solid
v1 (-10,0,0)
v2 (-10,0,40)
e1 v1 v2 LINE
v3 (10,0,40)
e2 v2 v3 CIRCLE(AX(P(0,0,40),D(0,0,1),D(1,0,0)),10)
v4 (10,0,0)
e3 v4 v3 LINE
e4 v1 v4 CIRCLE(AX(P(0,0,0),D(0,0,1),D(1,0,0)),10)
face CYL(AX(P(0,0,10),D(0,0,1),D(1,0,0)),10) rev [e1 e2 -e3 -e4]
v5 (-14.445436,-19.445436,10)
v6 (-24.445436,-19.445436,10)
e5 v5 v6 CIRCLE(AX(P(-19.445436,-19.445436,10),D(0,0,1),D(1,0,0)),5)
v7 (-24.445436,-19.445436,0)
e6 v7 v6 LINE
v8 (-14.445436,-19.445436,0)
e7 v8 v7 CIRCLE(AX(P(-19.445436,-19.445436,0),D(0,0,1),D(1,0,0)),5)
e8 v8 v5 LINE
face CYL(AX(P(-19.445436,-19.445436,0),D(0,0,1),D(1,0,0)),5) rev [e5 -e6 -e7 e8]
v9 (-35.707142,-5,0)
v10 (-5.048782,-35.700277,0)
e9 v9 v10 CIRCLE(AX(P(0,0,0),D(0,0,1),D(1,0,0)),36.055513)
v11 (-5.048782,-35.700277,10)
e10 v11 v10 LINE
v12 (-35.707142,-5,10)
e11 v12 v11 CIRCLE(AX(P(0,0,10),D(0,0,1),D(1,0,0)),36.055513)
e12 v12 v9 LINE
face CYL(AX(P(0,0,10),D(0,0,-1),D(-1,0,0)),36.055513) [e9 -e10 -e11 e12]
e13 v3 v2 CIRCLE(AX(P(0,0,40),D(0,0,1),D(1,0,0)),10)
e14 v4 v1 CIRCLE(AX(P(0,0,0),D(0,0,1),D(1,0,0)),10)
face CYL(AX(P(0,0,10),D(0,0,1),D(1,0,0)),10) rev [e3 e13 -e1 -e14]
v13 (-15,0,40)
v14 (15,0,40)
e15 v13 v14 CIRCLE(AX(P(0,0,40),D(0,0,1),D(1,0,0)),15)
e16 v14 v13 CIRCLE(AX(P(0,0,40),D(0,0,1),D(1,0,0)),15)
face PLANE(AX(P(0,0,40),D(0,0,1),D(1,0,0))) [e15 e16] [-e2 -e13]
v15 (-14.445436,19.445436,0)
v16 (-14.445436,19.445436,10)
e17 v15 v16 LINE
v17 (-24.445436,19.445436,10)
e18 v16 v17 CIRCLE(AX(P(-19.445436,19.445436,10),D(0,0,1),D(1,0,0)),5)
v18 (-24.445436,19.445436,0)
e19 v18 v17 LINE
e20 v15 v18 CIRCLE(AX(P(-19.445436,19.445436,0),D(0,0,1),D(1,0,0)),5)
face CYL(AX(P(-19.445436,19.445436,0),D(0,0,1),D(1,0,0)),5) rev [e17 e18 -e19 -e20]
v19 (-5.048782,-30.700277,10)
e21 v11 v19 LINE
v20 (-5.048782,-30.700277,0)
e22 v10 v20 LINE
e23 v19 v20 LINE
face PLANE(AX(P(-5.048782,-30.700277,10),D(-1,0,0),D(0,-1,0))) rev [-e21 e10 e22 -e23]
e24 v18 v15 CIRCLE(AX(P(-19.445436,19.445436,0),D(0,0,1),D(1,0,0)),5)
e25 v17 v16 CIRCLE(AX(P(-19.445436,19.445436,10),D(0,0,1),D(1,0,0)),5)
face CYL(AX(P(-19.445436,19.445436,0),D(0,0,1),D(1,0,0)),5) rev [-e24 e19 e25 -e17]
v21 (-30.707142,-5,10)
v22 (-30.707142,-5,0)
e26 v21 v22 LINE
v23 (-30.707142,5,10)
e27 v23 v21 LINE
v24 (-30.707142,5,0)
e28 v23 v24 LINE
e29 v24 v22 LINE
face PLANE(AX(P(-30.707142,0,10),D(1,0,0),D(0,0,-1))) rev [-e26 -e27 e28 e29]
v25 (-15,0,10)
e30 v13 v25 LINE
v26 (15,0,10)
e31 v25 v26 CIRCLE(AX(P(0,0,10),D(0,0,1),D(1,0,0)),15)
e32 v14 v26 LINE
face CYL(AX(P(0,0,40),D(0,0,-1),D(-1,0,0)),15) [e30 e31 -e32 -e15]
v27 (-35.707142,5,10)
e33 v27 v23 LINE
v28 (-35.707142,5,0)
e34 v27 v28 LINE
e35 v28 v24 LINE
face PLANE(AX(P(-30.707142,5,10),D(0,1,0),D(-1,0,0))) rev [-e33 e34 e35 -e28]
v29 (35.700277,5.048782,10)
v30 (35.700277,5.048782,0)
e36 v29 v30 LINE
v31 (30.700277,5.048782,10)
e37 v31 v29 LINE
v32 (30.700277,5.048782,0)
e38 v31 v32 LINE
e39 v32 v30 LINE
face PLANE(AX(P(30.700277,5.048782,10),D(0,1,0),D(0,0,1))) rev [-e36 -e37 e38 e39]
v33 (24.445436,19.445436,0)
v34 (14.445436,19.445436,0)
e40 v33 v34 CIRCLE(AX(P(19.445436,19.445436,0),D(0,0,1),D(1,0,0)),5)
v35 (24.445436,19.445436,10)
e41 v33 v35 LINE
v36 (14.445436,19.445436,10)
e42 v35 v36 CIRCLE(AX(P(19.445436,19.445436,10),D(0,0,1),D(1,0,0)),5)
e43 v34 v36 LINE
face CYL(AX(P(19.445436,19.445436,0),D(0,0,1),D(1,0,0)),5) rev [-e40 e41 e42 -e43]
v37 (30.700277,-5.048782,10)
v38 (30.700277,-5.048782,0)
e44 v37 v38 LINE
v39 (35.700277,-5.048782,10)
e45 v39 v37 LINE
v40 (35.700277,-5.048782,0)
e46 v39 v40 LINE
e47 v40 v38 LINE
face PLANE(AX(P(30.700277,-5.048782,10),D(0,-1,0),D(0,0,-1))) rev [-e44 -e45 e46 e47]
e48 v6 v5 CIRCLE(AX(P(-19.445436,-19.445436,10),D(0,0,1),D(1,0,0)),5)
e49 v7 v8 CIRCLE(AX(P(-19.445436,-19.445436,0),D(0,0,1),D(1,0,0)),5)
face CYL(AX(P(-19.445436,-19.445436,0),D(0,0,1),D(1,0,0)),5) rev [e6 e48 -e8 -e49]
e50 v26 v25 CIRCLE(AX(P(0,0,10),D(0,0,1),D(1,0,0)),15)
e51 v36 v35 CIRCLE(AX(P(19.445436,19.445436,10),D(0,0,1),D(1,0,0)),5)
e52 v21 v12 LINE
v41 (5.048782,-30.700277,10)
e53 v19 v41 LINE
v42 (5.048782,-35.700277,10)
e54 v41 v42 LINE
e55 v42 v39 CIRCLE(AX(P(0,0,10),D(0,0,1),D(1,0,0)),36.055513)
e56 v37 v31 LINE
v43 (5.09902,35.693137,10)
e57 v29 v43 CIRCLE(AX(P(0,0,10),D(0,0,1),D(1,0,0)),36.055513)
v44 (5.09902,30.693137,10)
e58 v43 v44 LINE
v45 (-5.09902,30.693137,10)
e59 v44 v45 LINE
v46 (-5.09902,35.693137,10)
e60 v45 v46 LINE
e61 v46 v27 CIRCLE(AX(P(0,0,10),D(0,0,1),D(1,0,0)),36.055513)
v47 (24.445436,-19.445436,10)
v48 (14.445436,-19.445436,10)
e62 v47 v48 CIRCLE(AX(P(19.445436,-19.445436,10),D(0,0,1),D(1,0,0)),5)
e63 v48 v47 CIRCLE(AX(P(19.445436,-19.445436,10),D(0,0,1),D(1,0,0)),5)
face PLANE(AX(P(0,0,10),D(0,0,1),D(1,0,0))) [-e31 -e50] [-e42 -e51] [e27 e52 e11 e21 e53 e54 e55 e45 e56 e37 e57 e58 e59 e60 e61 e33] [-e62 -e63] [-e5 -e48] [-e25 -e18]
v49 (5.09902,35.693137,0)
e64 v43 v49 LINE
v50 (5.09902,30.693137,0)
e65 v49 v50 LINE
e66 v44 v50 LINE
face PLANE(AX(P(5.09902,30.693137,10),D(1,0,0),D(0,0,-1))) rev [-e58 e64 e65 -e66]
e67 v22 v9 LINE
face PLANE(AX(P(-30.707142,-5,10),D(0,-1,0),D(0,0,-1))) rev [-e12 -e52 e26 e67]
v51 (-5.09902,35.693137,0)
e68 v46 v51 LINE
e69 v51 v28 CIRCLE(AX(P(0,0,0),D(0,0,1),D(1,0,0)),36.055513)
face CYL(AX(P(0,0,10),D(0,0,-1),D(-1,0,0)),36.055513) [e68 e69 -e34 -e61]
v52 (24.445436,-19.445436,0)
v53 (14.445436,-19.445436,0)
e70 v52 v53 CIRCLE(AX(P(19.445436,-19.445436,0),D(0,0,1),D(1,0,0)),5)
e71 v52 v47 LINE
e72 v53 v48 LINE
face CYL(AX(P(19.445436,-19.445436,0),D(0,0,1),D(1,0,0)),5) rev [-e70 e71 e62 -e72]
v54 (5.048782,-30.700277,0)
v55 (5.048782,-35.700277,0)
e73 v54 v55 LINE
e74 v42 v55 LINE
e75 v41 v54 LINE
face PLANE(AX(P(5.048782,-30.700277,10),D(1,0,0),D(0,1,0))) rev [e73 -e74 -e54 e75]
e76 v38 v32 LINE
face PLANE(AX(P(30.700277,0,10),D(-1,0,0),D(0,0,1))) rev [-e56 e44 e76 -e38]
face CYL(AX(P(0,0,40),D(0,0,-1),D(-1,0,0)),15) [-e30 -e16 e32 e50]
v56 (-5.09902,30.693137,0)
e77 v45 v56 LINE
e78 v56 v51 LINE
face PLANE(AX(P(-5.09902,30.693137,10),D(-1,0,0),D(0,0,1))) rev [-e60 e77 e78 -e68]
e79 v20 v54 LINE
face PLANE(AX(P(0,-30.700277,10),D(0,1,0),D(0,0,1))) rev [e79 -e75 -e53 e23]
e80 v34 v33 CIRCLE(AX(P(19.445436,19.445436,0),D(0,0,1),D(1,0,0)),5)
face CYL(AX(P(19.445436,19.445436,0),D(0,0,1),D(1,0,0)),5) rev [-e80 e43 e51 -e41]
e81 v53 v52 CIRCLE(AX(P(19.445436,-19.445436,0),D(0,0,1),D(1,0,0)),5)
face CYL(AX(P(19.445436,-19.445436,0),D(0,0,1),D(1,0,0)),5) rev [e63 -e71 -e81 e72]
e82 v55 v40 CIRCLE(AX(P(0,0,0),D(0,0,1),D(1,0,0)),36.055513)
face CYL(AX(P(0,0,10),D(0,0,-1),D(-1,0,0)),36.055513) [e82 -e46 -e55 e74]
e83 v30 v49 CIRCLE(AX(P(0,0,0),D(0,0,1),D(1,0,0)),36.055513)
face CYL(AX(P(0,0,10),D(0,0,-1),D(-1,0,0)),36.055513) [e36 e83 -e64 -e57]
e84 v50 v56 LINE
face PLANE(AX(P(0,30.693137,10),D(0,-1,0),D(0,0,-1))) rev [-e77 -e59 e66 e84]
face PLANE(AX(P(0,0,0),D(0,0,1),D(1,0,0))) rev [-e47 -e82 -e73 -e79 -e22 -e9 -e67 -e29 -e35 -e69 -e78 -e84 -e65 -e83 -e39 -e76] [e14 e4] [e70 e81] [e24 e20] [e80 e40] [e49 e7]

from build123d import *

# Parameters (mm, degrees)
FLANGE_PLATE_DEPTH         = 10
MOUNTING_HOLES_SKETCH_R    = 5
MOUNTING_HOLES_4X_10_DEPTH = 10
HUB_SKETCH_R               = 15
HUB_30_DEPTH               = 30
HUB_BORE_SKETCH_R          = 10
HUB_BORE_20_DEPTH          = 30
FLANGE_BORE_SKETCH_R       = 10
FLANGE_BORE_20_DEPTH       = 30


with BuildPart() as part:
    # Flange Profile Sketch → Flange Plate (new body)
    with BuildSketch(Plane.XY):
        with BuildLine():
            Line((0, 30.693136595), (5.099019514, 30.693136595))
            Line((5.099019514, 30.693136595), (5.099019514, 35.693136595))
            ThreePointArc((5.099019514, 35.693136595), (25.513031554, 25.477150958), (35.700277365, 5.048781643))
            Line((35.700277365, 5.048781643), (30.700277365, 5.048781643))
            Line((30.700277365, 5.048781643), (30.700277365, 0))
            Line((30.700277365, 0), (30.700277365, -5.048781643))
            Line((30.700277365, -5.048781643), (35.700277365, -5.048781643))
            ThreePointArc((35.700277365, -5.048781643), (25.495097568, -25.495097568), (5.048781643, -35.700277365))
            Line((5.048781643, -35.700277365), (5.048781643, -30.700277365))
            Line((5.048781643, -30.700277365), (0, -30.700277365))
            Line((0, -30.700277365), (-5.048781643, -30.700277365))
            Line((-5.048781643, -30.700277365), (-5.048781643, -35.700277365))
            ThreePointArc((-5.048781643, -35.700277365), (-25.512508471, -25.477674767), (-35.707142143, -5))
            Line((-35.707142143, -5), (-30.707142143, -5))
            Line((-30.707142143, -5), (-30.707142143, 0))
            Line((-30.707142143, 0), (-30.707142143, 5))
            Line((-30.707142143, 5), (-35.707142143, 5))
            ThreePointArc((-35.707142143, 5), (-25.530430192, 25.45971591), (-5.099019514, 35.693136595))
            Line((-5.099019514, 35.693136595), (-5.099019514, 30.693136595))
            Line((-5.099019514, 30.693136595), (0, 30.693136595))
        make_face()
    extrude(amount=FLANGE_PLATE_DEPTH)

    # Mounting Holes Sketch → Mounting Holes 4xØ10 (cut)
    with BuildSketch(Plane.XY.offset(10)):
        with Locations((19.445436483, 19.445436483)):
            Circle(MOUNTING_HOLES_SKETCH_R)
        with Locations((19.445436483, -19.445436483)):
            Circle(MOUNTING_HOLES_SKETCH_R)
        with Locations((-19.445436483, -19.445436483)):
            Circle(MOUNTING_HOLES_SKETCH_R)
        with Locations((-19.445436483, 19.445436483)):
            Circle(MOUNTING_HOLES_SKETCH_R)
    extrude(amount=-MOUNTING_HOLES_4X_10_DEPTH, mode=Mode.SUBTRACT)

    # Hub Sketch → Hub Ø30 (add)
    with BuildSketch(Plane.XY.offset(10)):
        Circle(HUB_SKETCH_R)
    extrude(amount=HUB_30_DEPTH)

    # Hub Bore Sketch → Hub Bore Ø20 (cut)
    with BuildSketch(Plane.XY.offset(40)):
        Circle(HUB_BORE_SKETCH_R)
    extrude(amount=-HUB_BORE_20_DEPTH, mode=Mode.SUBTRACT)

    # Flange Bore Sketch → Flange Bore Ø20 (cut)
    with BuildSketch(Plane.XY.offset(10)):
        Circle(FLANGE_BORE_SKETCH_R)
    extrude(amount=-FLANGE_BORE_20_DEPTH, mode=Mode.SUBTRACT)


solid = part.part
